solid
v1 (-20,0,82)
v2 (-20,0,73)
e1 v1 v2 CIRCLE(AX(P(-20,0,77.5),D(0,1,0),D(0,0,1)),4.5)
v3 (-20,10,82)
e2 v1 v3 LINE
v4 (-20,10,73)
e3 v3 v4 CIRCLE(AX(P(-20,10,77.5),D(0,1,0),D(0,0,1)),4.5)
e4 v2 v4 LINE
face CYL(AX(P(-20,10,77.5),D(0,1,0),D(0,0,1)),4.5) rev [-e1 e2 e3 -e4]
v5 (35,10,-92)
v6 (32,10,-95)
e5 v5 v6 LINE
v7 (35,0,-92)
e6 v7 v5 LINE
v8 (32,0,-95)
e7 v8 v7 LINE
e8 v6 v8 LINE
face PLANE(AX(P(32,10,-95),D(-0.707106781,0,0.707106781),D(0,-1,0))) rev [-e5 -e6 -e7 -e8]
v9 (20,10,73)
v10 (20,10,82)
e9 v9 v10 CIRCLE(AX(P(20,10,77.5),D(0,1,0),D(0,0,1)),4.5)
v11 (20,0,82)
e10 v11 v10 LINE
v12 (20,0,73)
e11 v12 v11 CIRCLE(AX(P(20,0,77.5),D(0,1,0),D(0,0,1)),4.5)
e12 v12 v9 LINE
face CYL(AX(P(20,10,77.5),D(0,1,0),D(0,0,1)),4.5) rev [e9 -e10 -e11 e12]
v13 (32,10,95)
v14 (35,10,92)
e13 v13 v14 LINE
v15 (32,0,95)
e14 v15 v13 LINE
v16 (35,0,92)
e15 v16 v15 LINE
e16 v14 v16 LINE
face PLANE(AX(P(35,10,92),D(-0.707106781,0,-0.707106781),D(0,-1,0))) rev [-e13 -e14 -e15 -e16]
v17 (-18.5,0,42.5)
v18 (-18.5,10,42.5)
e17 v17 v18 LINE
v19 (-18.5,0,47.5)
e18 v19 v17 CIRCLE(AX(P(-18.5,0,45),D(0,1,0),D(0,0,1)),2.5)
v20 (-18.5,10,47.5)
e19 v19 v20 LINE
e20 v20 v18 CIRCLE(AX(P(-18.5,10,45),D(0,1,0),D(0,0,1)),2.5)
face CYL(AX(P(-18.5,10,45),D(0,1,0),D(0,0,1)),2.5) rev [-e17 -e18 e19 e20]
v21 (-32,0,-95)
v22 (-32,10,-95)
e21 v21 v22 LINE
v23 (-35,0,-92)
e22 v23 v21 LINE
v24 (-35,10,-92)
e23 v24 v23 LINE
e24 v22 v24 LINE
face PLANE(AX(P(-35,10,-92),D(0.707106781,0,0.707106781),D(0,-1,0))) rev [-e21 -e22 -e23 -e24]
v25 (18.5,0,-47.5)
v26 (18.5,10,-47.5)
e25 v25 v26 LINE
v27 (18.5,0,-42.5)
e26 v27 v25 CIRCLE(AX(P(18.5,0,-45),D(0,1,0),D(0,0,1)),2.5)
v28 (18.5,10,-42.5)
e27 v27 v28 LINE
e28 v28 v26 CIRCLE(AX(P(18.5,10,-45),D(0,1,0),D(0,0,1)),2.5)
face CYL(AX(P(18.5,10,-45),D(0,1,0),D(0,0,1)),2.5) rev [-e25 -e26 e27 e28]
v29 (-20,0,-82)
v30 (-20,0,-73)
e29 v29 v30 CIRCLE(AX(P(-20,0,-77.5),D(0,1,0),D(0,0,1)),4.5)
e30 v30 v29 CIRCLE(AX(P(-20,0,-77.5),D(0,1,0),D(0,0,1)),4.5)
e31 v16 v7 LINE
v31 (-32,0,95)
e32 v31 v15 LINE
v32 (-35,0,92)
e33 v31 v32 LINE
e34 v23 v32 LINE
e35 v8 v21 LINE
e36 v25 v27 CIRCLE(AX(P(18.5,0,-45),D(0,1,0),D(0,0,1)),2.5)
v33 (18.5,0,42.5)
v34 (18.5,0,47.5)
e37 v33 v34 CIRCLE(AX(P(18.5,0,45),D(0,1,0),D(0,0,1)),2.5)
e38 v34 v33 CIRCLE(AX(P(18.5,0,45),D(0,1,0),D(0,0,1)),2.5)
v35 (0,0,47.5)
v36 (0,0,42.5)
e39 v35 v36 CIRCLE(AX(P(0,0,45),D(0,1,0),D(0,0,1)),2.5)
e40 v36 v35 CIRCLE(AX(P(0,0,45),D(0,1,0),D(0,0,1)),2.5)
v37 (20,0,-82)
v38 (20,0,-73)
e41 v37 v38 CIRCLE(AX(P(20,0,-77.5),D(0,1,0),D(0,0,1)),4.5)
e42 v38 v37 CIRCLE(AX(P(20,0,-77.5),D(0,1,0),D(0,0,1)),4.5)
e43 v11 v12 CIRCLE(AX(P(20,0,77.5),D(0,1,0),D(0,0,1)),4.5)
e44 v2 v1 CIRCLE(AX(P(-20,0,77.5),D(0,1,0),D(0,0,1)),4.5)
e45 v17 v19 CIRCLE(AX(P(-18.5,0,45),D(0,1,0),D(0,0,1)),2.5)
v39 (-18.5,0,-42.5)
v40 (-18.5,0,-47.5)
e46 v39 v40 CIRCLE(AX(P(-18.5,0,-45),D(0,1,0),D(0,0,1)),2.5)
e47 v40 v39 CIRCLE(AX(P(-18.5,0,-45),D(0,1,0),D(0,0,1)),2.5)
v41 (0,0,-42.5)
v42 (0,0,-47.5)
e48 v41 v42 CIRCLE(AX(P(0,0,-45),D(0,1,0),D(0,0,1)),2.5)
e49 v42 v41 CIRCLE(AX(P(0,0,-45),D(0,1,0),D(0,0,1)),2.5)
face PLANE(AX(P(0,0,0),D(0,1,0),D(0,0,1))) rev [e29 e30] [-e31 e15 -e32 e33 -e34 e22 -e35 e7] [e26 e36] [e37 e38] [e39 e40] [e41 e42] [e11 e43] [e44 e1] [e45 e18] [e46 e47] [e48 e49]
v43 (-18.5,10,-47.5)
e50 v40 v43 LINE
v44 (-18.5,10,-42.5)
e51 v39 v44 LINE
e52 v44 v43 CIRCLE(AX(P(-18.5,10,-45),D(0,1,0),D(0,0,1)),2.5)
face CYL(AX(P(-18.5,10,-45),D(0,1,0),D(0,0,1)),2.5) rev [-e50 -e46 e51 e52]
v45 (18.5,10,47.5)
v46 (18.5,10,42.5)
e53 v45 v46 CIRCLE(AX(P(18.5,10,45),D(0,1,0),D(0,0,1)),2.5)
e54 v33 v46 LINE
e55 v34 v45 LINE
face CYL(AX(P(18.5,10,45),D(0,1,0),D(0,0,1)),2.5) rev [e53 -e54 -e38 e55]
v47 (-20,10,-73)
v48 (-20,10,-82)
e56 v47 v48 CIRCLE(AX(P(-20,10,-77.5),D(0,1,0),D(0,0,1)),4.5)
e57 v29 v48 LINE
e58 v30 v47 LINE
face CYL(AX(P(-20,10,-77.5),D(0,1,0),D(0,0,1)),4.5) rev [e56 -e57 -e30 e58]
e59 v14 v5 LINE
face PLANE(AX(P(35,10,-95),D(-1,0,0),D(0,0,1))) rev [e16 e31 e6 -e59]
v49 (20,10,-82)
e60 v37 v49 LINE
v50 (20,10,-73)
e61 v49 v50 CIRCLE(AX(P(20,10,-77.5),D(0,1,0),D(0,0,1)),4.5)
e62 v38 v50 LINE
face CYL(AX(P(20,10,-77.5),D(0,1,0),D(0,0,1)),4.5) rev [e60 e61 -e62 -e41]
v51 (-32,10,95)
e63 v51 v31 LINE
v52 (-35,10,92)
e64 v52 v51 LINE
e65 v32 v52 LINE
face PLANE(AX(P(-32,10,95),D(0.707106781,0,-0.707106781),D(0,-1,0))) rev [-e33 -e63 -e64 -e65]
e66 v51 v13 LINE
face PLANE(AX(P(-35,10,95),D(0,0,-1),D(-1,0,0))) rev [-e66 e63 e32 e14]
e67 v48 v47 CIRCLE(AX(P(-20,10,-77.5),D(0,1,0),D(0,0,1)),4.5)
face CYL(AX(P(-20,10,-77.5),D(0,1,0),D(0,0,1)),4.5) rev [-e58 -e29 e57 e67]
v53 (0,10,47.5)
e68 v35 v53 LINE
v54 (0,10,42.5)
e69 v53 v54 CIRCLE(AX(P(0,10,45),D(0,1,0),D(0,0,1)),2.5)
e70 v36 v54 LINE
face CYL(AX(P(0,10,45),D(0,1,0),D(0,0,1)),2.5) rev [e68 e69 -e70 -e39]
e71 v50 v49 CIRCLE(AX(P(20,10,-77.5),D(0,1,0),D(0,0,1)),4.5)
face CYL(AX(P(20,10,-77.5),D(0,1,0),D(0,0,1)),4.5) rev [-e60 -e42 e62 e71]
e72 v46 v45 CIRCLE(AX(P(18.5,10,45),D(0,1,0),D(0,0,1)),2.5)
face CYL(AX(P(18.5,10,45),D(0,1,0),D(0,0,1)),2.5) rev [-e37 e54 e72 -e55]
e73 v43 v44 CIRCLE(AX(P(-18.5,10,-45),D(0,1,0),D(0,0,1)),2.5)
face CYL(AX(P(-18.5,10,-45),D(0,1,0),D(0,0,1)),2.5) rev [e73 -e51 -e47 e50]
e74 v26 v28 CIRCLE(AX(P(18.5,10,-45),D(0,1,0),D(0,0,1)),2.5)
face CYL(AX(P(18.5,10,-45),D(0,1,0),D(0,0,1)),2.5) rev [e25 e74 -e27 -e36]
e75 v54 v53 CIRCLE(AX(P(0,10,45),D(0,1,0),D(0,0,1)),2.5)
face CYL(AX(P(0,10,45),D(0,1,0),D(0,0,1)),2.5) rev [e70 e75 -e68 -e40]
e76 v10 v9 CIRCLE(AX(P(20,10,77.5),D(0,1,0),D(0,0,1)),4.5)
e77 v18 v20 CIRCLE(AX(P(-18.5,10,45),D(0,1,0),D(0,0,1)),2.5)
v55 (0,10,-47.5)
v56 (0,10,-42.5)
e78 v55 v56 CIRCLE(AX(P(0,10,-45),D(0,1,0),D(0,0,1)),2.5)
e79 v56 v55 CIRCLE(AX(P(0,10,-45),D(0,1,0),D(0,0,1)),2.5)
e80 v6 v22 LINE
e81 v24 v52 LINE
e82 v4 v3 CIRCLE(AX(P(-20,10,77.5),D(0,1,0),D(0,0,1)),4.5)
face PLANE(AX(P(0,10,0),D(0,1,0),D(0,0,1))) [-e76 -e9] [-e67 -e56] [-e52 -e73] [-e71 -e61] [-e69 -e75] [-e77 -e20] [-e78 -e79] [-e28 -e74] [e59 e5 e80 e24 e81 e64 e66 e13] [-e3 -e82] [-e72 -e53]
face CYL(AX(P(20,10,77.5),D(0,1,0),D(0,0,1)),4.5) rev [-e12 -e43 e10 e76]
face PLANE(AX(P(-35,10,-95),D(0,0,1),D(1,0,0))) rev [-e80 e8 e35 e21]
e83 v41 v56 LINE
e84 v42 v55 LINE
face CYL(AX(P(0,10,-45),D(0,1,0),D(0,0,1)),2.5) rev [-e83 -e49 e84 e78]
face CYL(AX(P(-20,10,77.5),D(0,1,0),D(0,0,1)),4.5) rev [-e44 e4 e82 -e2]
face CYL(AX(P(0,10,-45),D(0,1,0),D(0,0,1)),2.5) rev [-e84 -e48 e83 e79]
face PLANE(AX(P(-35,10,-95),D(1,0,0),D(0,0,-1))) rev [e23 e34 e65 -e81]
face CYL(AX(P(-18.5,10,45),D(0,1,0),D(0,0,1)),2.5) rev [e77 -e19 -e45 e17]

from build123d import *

# Parameters (mm, degrees)
SKETCH_1_W            = 70
SKETCH_1_H            = 190
EXTRUDE_1_DEPTH       = 10
HOLE_WIZARD_M6_1_D    = 5
HOLE_WIZARD_9_0_9_1_D = 9
CHAMFER_1_SIZE        = 3


with BuildPart() as part:
    # 草图1 → 凸台-拉伸1 (new body)
    with BuildSketch(Plane(origin=(0, 0, 0), x_dir=(1, 0, 0), z_dir=(0, 1, 0))):
        Rectangle(SKETCH_1_W, SKETCH_1_H)
    extrude(amount=EXTRUDE_1_DEPTH)

    # M6 螺纹孔1 (through all)
    with Locations(Plane(origin=(0, 10, 0), x_dir=(1, 0, 0), z_dir=(0, 1, 0))):
        with Locations((18.5, 45), (-18.5, 45), (0, 45), (0, -45), (-18.5, -45), (18.5, -45)):
            Hole(HOLE_WIZARD_M6_1_D / 2)

    # Ø9.0 (9) 直径孔1 (through all)
    with Locations(Plane(origin=(0, 10, 0), x_dir=(1, 0, 0), z_dir=(0, 1, 0))):
        with Locations((-20, 77.5), (20, 77.5), (20, -77.5), (-20, -77.5)):
            Hole(HOLE_WIZARD_9_0_9_1_D / 2)

    # 倒角1
    chamfer_1_edges = [part.edges().sort_by_distance(p)[0] for p in [
        (35, 5, 95),
        (-35, 5, 95),
        (-35, 5, -95),
        (35, 5, -95),
    ]]
    chamfer(chamfer_1_edges, length=CHAMFER_1_SIZE)


solid = part.part
